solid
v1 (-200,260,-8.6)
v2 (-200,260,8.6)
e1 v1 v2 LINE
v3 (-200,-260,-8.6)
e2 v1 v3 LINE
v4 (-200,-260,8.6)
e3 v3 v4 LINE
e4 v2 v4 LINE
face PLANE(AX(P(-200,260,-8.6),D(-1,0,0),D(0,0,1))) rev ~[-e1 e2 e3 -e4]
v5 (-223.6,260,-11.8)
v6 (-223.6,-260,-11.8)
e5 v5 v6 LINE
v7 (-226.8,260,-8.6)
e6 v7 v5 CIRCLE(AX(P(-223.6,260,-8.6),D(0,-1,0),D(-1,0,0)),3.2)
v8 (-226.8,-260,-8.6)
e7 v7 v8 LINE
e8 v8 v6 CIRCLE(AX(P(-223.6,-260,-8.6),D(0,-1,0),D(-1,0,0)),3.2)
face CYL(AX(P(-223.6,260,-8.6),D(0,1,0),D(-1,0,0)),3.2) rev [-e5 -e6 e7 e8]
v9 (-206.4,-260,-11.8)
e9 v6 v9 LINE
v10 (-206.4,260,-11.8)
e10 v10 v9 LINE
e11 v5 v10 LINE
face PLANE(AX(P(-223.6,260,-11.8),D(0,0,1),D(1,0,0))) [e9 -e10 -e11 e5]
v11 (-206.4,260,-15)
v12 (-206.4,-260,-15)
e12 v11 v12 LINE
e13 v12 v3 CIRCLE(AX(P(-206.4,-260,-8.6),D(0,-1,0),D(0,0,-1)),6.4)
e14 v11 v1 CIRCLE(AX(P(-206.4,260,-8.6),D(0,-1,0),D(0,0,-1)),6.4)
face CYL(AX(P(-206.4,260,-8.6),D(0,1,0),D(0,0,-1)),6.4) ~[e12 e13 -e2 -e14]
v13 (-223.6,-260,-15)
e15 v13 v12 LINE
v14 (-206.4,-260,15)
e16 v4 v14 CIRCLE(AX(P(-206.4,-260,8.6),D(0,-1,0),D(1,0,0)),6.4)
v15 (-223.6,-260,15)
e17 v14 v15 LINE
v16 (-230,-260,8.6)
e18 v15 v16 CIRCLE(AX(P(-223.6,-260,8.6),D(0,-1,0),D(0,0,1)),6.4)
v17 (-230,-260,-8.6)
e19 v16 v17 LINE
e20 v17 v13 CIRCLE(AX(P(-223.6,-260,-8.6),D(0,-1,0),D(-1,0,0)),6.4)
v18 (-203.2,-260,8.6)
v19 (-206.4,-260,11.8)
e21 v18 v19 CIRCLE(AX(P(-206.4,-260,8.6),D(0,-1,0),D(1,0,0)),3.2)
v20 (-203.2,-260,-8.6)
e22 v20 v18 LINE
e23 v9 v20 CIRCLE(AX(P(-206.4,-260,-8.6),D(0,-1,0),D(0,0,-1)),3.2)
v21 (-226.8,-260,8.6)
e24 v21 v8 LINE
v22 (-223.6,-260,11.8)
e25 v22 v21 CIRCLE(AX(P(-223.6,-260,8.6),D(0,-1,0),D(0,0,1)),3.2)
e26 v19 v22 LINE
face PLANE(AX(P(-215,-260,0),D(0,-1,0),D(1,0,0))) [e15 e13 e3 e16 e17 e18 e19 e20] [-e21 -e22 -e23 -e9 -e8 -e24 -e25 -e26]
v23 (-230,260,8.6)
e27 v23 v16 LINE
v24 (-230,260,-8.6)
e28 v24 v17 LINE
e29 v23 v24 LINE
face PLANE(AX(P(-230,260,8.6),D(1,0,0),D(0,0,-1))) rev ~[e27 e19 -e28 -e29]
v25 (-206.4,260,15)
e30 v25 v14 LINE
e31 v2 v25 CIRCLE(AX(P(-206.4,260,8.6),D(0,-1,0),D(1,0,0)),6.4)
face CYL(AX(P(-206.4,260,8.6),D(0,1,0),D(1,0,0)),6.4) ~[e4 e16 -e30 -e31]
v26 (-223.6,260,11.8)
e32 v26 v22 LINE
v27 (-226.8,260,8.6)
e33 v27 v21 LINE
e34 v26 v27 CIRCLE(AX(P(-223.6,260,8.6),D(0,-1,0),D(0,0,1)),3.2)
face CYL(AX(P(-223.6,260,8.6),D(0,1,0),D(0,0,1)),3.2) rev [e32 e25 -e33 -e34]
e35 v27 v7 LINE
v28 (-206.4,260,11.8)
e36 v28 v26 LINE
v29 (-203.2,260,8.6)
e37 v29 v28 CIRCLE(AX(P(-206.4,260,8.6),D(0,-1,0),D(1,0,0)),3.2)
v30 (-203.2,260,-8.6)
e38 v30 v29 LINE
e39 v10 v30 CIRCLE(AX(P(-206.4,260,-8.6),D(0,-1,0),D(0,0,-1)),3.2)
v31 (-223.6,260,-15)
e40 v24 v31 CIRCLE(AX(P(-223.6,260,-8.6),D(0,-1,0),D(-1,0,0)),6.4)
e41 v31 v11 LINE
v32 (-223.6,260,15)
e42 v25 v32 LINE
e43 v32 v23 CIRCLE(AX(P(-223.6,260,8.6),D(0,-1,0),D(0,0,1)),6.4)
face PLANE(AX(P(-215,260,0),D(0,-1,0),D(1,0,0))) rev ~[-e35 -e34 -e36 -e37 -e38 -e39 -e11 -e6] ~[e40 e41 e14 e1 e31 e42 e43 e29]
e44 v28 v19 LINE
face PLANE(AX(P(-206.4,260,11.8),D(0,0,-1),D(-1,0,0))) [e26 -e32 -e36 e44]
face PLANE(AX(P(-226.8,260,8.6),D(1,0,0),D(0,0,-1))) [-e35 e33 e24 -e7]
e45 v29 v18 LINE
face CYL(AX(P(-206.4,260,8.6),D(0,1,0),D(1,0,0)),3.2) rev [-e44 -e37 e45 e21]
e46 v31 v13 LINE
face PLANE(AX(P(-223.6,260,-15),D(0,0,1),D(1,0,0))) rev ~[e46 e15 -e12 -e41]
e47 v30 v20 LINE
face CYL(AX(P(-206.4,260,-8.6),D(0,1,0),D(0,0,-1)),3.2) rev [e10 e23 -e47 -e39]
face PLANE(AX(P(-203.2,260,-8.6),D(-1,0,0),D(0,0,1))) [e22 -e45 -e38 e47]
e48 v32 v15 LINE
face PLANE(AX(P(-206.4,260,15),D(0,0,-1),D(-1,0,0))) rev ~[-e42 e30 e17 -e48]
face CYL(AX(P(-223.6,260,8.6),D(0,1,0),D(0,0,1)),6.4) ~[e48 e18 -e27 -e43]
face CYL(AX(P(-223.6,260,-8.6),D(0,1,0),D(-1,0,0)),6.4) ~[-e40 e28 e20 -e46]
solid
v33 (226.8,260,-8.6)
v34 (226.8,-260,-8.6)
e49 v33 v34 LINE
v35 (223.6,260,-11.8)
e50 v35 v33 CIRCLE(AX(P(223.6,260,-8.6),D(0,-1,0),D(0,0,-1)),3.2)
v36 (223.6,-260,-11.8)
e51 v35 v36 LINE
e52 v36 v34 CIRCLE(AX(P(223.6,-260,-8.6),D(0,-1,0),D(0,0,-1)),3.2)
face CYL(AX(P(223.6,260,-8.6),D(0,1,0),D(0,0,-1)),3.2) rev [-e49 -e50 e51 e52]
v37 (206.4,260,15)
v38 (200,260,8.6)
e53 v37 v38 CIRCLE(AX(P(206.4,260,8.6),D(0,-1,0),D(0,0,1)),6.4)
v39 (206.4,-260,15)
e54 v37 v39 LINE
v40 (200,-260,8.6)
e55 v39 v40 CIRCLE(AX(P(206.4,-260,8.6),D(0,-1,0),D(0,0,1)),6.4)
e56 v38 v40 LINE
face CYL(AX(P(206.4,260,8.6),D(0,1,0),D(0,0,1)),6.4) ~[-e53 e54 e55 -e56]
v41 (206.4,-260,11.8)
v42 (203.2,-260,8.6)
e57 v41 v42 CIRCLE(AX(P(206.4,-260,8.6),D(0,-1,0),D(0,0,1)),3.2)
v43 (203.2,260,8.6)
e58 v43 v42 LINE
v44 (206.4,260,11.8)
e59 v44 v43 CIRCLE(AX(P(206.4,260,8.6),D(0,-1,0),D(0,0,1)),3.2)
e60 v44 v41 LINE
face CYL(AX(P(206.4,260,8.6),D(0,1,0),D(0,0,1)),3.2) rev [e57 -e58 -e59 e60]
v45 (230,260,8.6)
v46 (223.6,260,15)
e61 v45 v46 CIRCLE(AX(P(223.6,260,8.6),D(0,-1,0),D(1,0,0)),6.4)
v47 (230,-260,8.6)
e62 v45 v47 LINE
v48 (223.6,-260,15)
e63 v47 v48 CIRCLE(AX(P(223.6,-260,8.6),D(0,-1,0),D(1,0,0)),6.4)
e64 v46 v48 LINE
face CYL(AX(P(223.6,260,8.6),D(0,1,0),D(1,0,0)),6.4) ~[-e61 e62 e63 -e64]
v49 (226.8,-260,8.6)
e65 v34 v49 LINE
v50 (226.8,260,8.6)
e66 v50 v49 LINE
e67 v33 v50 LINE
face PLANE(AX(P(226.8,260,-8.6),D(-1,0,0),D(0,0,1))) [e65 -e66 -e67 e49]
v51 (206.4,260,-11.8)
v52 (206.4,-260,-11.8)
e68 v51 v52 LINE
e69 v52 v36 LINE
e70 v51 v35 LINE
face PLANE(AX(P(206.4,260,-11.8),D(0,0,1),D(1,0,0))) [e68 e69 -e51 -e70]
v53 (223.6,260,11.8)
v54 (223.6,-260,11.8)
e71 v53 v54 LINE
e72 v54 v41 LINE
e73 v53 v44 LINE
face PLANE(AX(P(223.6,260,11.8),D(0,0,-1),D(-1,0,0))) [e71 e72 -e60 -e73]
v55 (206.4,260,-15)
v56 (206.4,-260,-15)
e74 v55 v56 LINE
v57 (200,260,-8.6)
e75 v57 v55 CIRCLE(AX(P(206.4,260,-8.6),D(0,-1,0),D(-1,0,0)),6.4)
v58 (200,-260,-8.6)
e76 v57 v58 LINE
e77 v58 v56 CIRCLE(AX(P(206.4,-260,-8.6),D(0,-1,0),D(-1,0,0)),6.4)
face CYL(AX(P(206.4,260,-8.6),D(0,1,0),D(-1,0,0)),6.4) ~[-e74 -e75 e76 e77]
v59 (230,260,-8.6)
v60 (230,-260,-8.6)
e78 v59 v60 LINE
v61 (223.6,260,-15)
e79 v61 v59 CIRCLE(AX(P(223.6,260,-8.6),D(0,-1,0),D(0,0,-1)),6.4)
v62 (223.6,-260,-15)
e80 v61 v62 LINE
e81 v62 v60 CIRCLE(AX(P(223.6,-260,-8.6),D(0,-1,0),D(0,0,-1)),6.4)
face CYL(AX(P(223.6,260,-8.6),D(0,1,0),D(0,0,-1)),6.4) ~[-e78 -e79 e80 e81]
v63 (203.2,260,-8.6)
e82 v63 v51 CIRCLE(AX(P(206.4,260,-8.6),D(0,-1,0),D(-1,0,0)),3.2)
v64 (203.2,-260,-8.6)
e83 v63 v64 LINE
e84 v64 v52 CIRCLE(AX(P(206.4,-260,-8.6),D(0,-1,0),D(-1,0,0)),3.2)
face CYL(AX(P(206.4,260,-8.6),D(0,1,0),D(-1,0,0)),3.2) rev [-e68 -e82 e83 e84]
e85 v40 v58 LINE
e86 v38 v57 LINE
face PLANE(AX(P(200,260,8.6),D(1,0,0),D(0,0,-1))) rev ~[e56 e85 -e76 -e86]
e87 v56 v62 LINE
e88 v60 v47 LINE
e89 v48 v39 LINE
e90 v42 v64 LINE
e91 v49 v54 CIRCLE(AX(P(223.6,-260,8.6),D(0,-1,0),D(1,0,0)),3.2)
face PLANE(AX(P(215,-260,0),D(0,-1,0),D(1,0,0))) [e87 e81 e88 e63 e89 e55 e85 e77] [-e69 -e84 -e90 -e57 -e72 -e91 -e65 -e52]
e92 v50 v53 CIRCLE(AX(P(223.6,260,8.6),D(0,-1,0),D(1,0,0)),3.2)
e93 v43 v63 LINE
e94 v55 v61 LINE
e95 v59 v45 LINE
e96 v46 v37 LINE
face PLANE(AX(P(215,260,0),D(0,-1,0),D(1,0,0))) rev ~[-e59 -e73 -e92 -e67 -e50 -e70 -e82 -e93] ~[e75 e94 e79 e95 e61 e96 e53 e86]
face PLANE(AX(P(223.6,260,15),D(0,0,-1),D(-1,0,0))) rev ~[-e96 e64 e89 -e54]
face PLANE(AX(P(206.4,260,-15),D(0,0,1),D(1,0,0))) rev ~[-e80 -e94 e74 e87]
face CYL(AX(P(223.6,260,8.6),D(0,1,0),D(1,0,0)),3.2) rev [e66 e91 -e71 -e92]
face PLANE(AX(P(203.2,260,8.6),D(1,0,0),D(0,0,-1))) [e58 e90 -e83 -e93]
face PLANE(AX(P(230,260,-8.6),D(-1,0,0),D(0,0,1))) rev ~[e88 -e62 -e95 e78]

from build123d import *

# Parameters (mm, degrees)
SQUARE_TUBE_30_X_30_X_3_2_1_DEPTH   = 520
SQUARE_TUBE_30_X_30_X_3_2_1_2_DEPTH = 520


with BuildPart() as part:
    # Sketch1 → Square Tube 30 X 30 X 3.2(1) (new body)
    with BuildSketch(Plane(origin=(-215, 260, 0), x_dir=(1, 0, 0), z_dir=(0, -1, 0))):
        with BuildLine():
            Line((-8.6, -15), (8.6, -15))
            ThreePointArc((8.6, -15), (13.1254834, -13.1254834), (15, -8.6))
            Line((15, -8.6), (15, 8.6))
            ThreePointArc((15, 8.6), (13.1254834, 13.1254834), (8.6, 15))
            Line((8.6, 15), (-8.6, 15))
            ThreePointArc((-8.6, 15), (-13.1254834, 13.1254834), (-15, 8.6))
            Line((-15, 8.6), (-15, -8.6))
            ThreePointArc((-15, -8.6), (-13.1254834, -13.1254834), (-8.6, -15))
        make_face()
        with BuildLine():
            Line((-8.6, -11.8), (8.6, -11.8))
            ThreePointArc((8.6, -11.8), (10.8627417, -10.8627417), (11.8, -8.6))
            Line((11.8, -8.6), (11.8, 8.6))
            ThreePointArc((11.8, 8.6), (10.8627417, 10.8627417), (8.6, 11.8))
            Line((8.6, 11.8), (-8.6, 11.8))
            ThreePointArc((-8.6, 11.8), (-10.8627417, 10.8627417), (-11.8, 8.6))
            Line((-11.8, 8.6), (-11.8, -8.6))
            ThreePointArc((-11.8, -8.6), (-10.8627417, -10.8627417), (-8.6, -11.8))
        make_face(mode=Mode.SUBTRACT)
    extrude(amount=SQUARE_TUBE_30_X_30_X_3_2_1_DEPTH)


with BuildPart() as body_2:
    # Sketch1 on segment 2 (carried to segment 2) → Square Tube 30 X 30 X 3.2_1 2 (new body)
    with BuildSketch(Plane(origin=(215, 260, 0), x_dir=(1, 0, 0), z_dir=(0, -1, 0))):
        with BuildLine():
            Line((-8.6, -15), (8.6, -15))
            ThreePointArc((8.6, -15), (13.1254834, -13.1254834), (15, -8.6))
            Line((15, -8.6), (15, 8.6))
            ThreePointArc((15, 8.6), (13.1254834, 13.1254834), (8.6, 15))
            Line((8.6, 15), (-8.6, 15))
            ThreePointArc((-8.6, 15), (-13.1254834, 13.1254834), (-15, 8.6))
            Line((-15, 8.6), (-15, -8.6))
            ThreePointArc((-15, -8.6), (-13.1254834, -13.1254834), (-8.6, -15))
        make_face()
        with BuildLine():
            Line((-8.6, -11.8), (8.6, -11.8))
            ThreePointArc((8.6, -11.8), (10.8627417, -10.8627417), (11.8, -8.6))
            Line((11.8, -8.6), (11.8, 8.6))
            ThreePointArc((11.8, 8.6), (10.8627417, 10.8627417), (8.6, 11.8))
            Line((8.6, 11.8), (-8.6, 11.8))
            ThreePointArc((-8.6, 11.8), (-10.8627417, 10.8627417), (-11.8, 8.6))
            Line((-11.8, 8.6), (-11.8, -8.6))
            ThreePointArc((-11.8, -8.6), (-10.8627417, -10.8627417), (-8.6, -11.8))
        make_face(mode=Mode.SUBTRACT)
    extrude(amount=SQUARE_TUBE_30_X_30_X_3_2_1_2_DEPTH)


solid = Compound([part.part, body_2.part])
